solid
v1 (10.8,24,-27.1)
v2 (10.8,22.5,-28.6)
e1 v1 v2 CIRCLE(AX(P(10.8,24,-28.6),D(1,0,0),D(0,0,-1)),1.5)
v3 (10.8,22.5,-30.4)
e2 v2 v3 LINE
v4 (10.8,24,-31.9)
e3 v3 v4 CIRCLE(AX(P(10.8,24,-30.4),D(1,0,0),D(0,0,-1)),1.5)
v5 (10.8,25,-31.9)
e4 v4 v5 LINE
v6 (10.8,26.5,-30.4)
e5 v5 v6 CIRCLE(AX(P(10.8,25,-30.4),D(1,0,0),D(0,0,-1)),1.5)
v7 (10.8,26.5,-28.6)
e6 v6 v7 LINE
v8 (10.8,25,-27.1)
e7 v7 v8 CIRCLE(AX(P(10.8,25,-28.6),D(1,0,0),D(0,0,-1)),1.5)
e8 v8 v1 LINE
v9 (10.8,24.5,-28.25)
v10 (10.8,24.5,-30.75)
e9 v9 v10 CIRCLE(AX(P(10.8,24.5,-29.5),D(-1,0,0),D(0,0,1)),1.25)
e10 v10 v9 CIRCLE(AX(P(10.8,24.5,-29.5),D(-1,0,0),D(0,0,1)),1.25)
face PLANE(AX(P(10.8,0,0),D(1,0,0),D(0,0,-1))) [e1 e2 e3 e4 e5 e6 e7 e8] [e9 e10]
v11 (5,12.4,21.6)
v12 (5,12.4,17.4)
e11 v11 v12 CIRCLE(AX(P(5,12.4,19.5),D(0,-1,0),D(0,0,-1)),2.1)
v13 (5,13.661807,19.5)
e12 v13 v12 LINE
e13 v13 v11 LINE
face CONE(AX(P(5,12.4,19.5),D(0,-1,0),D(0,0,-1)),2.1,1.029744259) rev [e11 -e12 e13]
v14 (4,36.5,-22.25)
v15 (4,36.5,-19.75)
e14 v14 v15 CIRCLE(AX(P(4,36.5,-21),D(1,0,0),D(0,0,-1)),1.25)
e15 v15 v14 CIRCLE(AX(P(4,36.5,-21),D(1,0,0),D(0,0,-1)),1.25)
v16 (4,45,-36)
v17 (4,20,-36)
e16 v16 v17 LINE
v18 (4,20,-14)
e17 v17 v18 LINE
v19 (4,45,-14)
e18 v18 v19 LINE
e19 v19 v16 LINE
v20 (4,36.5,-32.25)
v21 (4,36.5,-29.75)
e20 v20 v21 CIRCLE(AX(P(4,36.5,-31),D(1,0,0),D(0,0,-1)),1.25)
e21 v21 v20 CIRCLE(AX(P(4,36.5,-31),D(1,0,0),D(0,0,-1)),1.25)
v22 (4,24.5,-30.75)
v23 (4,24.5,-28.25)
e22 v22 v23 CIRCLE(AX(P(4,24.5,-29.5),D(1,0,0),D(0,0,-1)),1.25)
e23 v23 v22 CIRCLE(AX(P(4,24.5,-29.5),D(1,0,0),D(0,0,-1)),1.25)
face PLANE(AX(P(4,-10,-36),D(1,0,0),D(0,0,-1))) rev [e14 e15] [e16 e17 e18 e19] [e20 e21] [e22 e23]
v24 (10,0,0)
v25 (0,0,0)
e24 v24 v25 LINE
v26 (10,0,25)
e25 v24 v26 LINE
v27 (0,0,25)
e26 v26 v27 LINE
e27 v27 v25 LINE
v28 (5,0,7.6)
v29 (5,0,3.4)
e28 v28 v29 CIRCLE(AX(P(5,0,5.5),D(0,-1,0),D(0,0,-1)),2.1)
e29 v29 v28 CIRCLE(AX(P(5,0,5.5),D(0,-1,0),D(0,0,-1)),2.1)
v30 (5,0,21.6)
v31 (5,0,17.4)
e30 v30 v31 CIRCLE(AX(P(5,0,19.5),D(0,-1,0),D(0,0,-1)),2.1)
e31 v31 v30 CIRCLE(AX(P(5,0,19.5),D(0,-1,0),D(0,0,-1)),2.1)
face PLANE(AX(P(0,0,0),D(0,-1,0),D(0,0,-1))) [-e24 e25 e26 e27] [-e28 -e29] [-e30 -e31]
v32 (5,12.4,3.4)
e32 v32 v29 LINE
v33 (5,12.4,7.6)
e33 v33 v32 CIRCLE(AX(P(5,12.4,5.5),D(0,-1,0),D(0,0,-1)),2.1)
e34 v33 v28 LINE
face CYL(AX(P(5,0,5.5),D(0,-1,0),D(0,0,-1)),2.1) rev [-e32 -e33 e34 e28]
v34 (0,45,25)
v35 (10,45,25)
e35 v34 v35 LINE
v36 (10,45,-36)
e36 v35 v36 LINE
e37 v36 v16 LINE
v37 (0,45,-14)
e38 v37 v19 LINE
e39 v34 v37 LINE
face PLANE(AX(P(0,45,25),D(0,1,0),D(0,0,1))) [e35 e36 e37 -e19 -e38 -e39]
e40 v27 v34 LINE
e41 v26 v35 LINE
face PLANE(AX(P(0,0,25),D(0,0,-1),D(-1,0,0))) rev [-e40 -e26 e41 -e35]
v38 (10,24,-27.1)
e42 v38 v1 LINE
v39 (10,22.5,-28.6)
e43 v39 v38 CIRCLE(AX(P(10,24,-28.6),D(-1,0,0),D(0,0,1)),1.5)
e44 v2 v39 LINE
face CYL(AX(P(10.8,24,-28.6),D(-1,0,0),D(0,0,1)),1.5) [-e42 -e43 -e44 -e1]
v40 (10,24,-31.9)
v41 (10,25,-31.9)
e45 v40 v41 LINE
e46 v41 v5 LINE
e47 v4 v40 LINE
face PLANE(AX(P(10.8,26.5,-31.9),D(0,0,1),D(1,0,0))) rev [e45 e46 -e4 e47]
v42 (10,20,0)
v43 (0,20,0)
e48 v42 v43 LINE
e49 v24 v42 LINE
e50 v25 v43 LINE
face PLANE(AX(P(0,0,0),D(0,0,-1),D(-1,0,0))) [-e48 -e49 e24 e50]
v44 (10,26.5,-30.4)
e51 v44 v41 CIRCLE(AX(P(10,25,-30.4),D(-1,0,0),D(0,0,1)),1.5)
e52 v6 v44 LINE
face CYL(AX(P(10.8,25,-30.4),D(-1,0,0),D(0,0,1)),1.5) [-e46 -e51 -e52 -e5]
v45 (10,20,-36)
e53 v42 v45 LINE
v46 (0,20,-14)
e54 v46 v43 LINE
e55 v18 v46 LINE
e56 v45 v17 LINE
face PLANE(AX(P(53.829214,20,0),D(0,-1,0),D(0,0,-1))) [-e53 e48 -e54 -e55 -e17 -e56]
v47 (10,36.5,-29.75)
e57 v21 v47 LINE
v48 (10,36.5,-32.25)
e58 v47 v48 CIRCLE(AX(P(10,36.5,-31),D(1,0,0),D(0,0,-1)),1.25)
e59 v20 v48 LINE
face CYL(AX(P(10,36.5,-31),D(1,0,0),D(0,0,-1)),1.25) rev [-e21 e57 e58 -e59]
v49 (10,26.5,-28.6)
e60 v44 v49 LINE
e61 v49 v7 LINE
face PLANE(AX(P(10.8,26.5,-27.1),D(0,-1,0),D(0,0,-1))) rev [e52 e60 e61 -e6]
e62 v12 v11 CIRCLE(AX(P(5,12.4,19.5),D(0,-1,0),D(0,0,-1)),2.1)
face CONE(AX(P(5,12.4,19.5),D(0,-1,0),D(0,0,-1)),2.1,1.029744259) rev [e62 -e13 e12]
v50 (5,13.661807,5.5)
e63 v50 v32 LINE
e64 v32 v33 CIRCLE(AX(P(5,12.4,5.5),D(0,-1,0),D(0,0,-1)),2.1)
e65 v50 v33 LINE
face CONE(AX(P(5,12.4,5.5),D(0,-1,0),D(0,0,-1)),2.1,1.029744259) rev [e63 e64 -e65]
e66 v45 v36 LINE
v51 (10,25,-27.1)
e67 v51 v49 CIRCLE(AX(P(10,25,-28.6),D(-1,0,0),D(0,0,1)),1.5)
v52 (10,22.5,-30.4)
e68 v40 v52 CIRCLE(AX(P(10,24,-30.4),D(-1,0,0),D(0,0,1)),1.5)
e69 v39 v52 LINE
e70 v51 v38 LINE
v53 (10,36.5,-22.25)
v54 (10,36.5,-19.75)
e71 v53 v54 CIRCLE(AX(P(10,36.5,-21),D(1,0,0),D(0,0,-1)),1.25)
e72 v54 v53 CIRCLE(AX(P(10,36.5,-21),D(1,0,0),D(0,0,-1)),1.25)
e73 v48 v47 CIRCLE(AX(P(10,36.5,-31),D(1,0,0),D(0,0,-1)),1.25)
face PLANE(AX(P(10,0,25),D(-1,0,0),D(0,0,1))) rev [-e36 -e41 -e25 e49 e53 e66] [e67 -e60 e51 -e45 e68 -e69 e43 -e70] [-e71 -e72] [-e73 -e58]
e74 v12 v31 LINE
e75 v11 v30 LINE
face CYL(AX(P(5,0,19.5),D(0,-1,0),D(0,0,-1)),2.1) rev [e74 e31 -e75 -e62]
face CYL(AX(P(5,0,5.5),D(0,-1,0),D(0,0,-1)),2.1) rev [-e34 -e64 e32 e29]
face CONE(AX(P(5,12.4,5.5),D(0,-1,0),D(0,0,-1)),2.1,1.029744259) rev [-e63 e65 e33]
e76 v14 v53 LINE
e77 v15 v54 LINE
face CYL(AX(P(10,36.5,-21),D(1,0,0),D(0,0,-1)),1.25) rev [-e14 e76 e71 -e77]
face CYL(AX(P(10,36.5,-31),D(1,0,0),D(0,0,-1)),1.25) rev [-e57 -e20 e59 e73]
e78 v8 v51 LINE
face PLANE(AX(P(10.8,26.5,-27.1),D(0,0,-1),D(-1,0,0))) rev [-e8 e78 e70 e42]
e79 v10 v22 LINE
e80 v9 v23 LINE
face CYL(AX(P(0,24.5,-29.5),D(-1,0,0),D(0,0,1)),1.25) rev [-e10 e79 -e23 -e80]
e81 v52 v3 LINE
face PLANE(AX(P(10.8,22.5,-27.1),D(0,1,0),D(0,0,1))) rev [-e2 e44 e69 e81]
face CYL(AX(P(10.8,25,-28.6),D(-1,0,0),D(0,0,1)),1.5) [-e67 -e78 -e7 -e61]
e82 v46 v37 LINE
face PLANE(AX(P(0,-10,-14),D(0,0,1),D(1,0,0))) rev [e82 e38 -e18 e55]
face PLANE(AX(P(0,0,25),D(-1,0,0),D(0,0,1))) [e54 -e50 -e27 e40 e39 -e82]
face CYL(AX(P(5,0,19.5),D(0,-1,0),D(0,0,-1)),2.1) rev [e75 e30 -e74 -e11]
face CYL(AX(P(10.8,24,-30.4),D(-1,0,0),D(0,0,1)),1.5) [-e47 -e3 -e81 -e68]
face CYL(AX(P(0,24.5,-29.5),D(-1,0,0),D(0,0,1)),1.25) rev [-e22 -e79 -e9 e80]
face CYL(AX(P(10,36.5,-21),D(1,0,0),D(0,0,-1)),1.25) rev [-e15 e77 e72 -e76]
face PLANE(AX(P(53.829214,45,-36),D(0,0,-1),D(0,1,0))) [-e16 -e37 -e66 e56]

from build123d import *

# Parameters (mm, degrees)
EXTRUDE_THIN1_DEPTH   = 25
SKETCH2_W             = 36
SKETCH2_H             = 25
BOSS_EXTRUDE1_DEPTH   = 10
SKETCH5_W             = 4
SKETCH5_H             = 22
CUT_EXTRUDE1_DEPTH    = 68.424031324
SKETCH6_W             = 93.972678959
SKETCH6_H             = 54.427614962
CUT_EXTRUDE2_DEPTH    = 10
M5_TAPPED_HOLE1_D     = 4.2
M5_TAPPED_HOLE1_DEPTH = 12.4
M5_TAPPED_HOLE1_TIP   = 1.2618073
M3_TAPPED_HOLE1_D     = 2.5
SKETCH12_W            = 4.8
SKETCH12_H            = 4
BOSS_EXTRUDE2_DEPTH   = 0.8
M3_TAPPED_HOLE2_D     = 2.5
FILLET1_R             = 1.5


with BuildPart() as part:
    # Sketch1 → Extrude-Thin1 (new body)
    with BuildSketch(Plane.XY):
        Polygon((-15, 0), (0, 0), (0, 45), (10, 45), (10, -10), (-15, -10), align=None)
    extrude(amount=EXTRUDE_THIN1_DEPTH)

    # Sketch2 → Boss-Extrude1 (add)
    with BuildSketch(Plane.ZY):
        with Locations((-18, 32.5)):
            Rectangle(SKETCH2_W, SKETCH2_H)
    extrude(amount=-BOSS_EXTRUDE1_DEPTH)

    # Sketch5 → Cut-Extrude1 (cut, through all)
    with BuildSketch(Plane(origin=(0, 45, 0), x_dir=(1, 0, 0), z_dir=(0, 1, 0))):
        with Locations((2, 25)):
            Rectangle(SKETCH5_W, SKETCH5_H)
    extrude(amount=-CUT_EXTRUDE1_DEPTH, mode=Mode.SUBTRACT)

    # Sketch6 → Cut-Extrude2 (cut)
    with BuildSketch(Plane.XZ.offset(10)):
        with Locations((-13.059524258, 16.160355611)):
            Rectangle(SKETCH6_W, SKETCH6_H)
    extrude(amount=-CUT_EXTRUDE2_DEPTH, mode=Mode.SUBTRACT)

    # M5 Tapped Hole1
    with Locations(Plane(origin=(0, 0, 0), x_dir=(-1, 0, 0), z_dir=(0, -1, 0))):
        with Locations((-5, -5.5), (-5, -19.5)):
            Hole(M5_TAPPED_HOLE1_D / 2, depth=M5_TAPPED_HOLE1_DEPTH)
            with Locations((0, 0, -(M5_TAPPED_HOLE1_DEPTH + M5_TAPPED_HOLE1_TIP / 2))):  # 118° drill point
                Cone(0, M5_TAPPED_HOLE1_D / 2, M5_TAPPED_HOLE1_TIP, mode=Mode.SUBTRACT)

    # M3 Tapped Hole1 (through all)
    with Locations(Plane(origin=(10, 0, 0), x_dir=(0, 0, -1), z_dir=(1, 0, 0))):
        with Locations((21, 36.5), (31, 36.5)):
            Hole(M3_TAPPED_HOLE1_D / 2)

    # Sketch12 → Boss-Extrude2 (add)
    with BuildSketch(Plane(origin=(10, 0, 0), x_dir=(0, 0, -1), z_dir=(1, 0, 0))):
        with Locations((29.5, 24.5)):
            Rectangle(SKETCH12_W, SKETCH12_H)
    extrude(amount=BOSS_EXTRUDE2_DEPTH)

    # M3 Tapped Hole2 (through all)
    with Locations(Plane.ZY):
        with Locations((-29.5, 24.5)):
            Hole(M3_TAPPED_HOLE2_D / 2)

    # Fillet1
    fillet1_edges = [part.edges().sort_by_distance(p)[0] for p in [
        (10.4, 22.5, -31.9),
        (10.4, 26.5, -31.9),
        (10.4, 26.5, -27.1),
        (10.4, 22.5, -27.1),
    ]]
    fillet(fillet1_edges, radius=FILLET1_R)


solid = part.part
